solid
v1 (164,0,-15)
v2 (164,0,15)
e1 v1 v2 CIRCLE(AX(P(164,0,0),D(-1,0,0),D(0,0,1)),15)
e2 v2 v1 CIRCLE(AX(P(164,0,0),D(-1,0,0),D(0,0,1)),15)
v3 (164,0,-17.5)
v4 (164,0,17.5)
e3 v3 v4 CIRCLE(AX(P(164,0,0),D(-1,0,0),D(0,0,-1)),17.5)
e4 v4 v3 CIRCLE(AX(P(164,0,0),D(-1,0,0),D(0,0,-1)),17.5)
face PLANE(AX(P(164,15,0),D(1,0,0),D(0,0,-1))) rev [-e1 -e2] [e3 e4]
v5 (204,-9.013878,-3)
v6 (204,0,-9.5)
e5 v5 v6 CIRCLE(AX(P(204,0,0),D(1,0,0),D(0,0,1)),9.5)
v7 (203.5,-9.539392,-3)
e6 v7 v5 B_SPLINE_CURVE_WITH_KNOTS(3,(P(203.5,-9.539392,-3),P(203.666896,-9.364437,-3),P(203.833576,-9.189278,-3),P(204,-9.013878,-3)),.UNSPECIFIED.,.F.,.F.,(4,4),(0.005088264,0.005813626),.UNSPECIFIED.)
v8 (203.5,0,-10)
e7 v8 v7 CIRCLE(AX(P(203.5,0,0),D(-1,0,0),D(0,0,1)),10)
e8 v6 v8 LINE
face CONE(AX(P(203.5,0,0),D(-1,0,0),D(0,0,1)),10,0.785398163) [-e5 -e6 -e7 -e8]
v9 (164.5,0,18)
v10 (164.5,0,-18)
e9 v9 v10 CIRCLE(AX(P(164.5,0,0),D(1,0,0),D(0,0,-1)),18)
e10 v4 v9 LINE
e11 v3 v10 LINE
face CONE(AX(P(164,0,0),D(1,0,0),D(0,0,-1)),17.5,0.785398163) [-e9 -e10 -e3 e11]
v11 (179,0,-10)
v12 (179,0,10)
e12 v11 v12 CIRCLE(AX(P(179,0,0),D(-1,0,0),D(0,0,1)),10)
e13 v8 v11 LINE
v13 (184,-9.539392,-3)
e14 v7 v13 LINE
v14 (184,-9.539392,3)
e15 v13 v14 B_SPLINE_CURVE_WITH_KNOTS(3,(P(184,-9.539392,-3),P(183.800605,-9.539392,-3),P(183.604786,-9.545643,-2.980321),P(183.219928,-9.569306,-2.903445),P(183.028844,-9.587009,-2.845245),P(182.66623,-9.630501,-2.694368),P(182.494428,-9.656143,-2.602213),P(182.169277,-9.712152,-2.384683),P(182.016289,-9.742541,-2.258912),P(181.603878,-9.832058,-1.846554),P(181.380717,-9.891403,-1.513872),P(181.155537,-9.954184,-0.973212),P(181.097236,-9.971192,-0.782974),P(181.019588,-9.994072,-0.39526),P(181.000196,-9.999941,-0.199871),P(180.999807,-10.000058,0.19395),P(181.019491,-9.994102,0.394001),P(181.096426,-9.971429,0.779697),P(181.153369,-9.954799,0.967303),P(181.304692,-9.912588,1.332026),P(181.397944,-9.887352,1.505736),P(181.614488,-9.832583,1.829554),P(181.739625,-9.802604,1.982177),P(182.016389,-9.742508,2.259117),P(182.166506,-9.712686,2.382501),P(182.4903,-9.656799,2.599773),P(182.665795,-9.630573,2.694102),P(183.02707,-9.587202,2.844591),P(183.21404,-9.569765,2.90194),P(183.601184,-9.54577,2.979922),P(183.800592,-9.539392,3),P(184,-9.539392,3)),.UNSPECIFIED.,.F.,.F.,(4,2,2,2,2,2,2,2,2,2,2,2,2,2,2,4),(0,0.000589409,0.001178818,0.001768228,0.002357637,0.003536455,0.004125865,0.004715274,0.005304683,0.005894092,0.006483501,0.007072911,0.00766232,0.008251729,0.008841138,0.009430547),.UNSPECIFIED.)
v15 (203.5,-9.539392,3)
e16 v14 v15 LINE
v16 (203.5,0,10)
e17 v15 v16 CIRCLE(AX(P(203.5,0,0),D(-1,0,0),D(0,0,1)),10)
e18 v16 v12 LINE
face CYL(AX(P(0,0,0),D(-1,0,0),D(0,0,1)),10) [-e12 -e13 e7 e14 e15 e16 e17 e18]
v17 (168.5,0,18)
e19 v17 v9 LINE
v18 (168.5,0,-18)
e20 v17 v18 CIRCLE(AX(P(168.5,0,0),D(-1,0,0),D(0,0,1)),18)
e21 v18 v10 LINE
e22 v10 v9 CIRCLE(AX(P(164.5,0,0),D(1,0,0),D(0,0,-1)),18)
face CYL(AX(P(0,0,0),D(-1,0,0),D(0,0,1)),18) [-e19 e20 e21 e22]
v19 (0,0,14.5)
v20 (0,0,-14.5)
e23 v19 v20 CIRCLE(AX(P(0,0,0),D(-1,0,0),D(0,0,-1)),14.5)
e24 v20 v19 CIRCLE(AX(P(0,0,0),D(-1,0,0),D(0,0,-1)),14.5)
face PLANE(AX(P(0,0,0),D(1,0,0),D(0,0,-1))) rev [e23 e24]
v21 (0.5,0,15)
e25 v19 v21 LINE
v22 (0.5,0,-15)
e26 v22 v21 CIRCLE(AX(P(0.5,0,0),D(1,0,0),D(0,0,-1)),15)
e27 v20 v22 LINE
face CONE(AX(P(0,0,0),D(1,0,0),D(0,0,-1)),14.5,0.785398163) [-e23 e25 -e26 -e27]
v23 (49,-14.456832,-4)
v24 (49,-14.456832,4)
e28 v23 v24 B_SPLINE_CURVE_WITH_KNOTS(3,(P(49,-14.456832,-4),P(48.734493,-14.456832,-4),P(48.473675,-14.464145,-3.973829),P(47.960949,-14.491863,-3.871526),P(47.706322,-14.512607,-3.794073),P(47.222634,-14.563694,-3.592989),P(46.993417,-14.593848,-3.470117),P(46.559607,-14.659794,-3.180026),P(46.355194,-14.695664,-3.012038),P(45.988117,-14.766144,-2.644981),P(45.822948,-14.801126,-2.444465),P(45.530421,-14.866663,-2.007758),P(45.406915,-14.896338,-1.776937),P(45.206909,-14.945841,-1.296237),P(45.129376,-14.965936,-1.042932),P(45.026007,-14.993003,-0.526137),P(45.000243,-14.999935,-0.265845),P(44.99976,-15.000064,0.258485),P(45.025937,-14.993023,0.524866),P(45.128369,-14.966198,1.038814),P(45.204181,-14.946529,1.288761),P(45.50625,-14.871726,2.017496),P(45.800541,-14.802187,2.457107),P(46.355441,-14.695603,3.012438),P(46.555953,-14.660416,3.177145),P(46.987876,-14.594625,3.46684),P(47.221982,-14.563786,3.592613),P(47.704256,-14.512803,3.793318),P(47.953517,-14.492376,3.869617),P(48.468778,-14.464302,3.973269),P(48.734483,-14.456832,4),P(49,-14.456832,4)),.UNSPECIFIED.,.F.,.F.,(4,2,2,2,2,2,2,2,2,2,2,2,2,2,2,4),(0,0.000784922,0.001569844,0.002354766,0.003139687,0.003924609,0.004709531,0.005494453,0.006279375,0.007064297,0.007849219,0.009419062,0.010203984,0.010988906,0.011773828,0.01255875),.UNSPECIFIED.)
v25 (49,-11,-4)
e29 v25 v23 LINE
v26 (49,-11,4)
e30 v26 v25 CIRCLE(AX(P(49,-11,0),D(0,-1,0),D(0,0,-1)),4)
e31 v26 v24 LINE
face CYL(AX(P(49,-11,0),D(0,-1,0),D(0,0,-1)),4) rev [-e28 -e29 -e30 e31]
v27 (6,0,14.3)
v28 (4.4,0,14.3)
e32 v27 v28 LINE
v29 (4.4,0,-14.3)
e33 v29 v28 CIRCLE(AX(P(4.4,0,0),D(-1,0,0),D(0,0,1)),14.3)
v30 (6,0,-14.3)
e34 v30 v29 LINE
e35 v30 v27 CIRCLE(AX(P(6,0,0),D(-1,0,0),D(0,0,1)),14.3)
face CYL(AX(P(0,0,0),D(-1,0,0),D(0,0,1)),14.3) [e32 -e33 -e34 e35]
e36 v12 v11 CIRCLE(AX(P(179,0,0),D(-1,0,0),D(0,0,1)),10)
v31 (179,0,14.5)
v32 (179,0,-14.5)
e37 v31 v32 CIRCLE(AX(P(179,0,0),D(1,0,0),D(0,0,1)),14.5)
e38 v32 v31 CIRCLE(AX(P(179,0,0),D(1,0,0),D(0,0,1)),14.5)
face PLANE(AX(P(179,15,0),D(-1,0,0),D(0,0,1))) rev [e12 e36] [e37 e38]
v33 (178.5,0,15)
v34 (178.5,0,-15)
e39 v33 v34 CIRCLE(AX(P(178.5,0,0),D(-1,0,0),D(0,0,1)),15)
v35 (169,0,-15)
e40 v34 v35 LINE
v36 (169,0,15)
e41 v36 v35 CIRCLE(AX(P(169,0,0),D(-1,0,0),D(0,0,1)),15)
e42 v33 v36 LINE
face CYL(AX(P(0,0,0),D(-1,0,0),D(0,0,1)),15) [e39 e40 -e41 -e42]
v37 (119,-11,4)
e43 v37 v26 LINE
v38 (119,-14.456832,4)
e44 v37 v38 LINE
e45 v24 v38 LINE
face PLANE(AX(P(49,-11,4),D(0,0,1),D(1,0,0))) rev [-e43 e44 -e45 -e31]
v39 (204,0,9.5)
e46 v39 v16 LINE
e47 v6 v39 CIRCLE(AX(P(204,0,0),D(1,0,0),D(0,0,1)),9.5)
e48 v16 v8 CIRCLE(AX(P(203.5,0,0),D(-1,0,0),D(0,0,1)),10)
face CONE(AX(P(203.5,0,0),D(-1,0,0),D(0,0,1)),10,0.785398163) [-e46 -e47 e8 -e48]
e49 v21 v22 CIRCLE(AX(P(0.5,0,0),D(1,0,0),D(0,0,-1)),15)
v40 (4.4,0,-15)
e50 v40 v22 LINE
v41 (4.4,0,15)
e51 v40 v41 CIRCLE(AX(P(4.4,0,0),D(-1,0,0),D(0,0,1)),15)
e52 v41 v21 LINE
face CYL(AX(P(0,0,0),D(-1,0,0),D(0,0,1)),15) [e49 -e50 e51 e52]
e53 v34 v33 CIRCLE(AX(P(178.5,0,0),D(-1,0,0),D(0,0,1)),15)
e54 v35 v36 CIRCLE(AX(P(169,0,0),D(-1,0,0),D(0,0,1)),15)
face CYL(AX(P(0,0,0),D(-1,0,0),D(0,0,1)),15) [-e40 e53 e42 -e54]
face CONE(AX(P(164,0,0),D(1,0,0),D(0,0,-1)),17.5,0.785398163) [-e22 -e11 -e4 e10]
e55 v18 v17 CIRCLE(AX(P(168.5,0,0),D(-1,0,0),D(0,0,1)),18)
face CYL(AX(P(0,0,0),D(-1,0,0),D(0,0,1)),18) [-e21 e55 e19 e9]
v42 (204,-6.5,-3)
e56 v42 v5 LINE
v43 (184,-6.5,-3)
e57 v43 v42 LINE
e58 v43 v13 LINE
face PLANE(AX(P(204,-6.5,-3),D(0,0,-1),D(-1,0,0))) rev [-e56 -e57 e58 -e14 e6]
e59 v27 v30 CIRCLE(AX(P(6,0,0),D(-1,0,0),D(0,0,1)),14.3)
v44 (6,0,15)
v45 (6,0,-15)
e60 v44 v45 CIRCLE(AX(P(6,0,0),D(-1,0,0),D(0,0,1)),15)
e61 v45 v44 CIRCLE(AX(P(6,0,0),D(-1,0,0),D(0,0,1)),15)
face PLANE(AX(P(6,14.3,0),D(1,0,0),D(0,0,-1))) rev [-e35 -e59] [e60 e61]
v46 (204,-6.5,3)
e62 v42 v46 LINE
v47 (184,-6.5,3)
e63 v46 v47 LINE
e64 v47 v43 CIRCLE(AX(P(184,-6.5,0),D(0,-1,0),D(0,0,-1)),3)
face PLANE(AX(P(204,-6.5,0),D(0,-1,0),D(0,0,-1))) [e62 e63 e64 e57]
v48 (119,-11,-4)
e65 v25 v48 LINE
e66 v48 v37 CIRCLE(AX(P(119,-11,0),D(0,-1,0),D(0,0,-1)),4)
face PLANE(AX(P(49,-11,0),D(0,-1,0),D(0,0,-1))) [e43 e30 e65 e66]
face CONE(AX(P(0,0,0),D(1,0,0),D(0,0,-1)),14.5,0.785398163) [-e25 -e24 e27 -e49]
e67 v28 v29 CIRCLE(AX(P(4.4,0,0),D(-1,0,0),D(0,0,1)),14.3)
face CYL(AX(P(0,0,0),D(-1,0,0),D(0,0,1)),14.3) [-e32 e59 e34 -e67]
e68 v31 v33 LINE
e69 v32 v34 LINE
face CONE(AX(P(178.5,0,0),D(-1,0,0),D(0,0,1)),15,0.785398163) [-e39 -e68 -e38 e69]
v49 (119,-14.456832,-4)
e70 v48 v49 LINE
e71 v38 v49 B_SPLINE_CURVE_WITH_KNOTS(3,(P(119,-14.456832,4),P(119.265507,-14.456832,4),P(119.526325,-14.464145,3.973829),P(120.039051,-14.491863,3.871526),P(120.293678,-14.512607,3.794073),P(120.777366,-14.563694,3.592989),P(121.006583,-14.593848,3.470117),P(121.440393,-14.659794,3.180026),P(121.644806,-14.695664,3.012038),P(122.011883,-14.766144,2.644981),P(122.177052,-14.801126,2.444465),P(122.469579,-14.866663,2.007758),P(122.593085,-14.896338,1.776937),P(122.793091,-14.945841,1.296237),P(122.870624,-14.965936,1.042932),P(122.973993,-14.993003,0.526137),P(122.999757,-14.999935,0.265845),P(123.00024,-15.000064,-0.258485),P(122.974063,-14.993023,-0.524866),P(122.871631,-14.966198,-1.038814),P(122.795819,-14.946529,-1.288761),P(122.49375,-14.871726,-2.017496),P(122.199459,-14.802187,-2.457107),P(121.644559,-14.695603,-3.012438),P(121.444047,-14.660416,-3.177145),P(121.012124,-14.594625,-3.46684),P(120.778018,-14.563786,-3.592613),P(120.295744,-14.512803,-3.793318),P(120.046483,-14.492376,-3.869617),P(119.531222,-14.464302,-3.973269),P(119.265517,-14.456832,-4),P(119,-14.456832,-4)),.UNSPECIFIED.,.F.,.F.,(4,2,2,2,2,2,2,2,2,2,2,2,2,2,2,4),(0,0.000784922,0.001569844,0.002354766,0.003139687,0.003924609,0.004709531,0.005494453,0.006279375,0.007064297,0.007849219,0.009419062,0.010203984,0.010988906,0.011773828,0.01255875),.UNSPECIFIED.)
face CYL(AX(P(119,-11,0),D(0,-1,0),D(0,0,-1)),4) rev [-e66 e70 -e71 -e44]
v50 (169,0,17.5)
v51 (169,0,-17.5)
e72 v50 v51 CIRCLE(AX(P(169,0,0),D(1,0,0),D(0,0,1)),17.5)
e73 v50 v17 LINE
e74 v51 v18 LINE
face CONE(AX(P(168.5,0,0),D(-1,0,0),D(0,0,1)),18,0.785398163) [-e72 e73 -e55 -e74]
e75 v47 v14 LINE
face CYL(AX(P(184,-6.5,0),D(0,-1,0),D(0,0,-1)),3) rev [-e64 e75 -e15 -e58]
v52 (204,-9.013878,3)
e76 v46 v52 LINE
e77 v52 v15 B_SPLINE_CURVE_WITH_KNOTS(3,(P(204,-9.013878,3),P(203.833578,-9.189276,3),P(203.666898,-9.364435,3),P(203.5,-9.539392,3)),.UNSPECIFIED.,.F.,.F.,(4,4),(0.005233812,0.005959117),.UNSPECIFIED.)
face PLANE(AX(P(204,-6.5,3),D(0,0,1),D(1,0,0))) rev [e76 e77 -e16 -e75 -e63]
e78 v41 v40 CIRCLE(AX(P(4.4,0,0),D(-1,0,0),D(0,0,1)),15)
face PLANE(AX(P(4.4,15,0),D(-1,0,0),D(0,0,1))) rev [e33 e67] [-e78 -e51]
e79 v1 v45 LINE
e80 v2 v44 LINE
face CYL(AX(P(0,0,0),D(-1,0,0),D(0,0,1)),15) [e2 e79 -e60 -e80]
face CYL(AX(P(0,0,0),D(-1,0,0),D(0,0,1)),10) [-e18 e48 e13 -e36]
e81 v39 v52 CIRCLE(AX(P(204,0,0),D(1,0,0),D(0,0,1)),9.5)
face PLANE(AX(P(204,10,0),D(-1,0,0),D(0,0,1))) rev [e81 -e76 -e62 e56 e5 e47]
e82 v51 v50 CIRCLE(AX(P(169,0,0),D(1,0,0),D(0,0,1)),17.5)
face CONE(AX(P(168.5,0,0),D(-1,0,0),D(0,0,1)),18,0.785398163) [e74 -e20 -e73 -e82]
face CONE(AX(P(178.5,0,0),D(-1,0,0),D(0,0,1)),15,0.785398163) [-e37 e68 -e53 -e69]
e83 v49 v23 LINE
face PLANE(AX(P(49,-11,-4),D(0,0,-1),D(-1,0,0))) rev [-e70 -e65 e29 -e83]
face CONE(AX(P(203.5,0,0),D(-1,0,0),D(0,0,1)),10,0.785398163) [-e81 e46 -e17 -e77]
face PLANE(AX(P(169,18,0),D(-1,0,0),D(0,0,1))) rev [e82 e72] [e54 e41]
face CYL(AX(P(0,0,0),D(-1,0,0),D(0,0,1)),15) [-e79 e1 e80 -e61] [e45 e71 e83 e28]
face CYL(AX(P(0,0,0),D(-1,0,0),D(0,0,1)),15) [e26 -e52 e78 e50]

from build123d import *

# Parameters (mm, degrees)
CHAMFER_1_SIZE      = 0.5
CUT_EXTRUDE_1_DEPTH = 4
CUT_EXTRUDE_2_DEPTH = 3.5


with BuildPart() as part:
    # 草图1 → 旋转1 (revolve)
    with BuildSketch(Plane.XY, mode=Mode.PRIVATE) as revolve_1_sk:
        Polygon((0, 0), (0, 15), (4.4, 15), (4.4, 14.3), (6, 14.3), (6, 15), (164, 15), (164, 18), (169, 18), (169, 15), (179, 15), (179, 10), (204, 10), (204, 0), align=None)
    revolve(revolve_1_sk.sketch.rotate(Axis((0, 0, 0), (1, 0, 0)), 90), axis=Axis((0, 0, 0), (1, 0, 0)))

    # 倒角1
    chamfer_1_edges = [part.edges().sort_by_distance(p)[0] for p in [
        (204, 0, -10),
        (179, 0, -15),
        (169, 0, -18),
        (164, 0, -18),
        (0, 0, -15),
    ]]
    chamfer(chamfer_1_edges, length=CHAMFER_1_SIZE)

    # 草图2 → 切除-拉伸1 (cut)
    with BuildSketch(Plane(origin=(0, -15, 0), x_dir=(-1, 0, 0), z_dir=(0, -1, 0))):
        with BuildLine():
            Line((-49, -4), (-119, -4))
            ThreePointArc((-119, -4), (-123, 0), (-119, 4))
            Line((-119, 4), (-49, 4))
            ThreePointArc((-49, 4), (-45, 0), (-49, -4))
        make_face()
    extrude(amount=-CUT_EXTRUDE_1_DEPTH, mode=Mode.SUBTRACT)

    # 草图3 → 切除-拉伸2 (cut)
    with BuildSketch(Plane(origin=(0, -10, 0), x_dir=(-1, 0, 0), z_dir=(0, -1, 0))):
        with BuildLine():
            Line((-204, 3), (-184, 3))
            ThreePointArc((-184, 3), (-181, 0), (-184, -3))
            Line((-184, -3), (-204, -3))
            ThreePointArc((-204, -3), (-207, 0), (-204, 3))
        make_face()
    extrude(amount=-CUT_EXTRUDE_2_DEPTH, mode=Mode.SUBTRACT)


solid = part.part
